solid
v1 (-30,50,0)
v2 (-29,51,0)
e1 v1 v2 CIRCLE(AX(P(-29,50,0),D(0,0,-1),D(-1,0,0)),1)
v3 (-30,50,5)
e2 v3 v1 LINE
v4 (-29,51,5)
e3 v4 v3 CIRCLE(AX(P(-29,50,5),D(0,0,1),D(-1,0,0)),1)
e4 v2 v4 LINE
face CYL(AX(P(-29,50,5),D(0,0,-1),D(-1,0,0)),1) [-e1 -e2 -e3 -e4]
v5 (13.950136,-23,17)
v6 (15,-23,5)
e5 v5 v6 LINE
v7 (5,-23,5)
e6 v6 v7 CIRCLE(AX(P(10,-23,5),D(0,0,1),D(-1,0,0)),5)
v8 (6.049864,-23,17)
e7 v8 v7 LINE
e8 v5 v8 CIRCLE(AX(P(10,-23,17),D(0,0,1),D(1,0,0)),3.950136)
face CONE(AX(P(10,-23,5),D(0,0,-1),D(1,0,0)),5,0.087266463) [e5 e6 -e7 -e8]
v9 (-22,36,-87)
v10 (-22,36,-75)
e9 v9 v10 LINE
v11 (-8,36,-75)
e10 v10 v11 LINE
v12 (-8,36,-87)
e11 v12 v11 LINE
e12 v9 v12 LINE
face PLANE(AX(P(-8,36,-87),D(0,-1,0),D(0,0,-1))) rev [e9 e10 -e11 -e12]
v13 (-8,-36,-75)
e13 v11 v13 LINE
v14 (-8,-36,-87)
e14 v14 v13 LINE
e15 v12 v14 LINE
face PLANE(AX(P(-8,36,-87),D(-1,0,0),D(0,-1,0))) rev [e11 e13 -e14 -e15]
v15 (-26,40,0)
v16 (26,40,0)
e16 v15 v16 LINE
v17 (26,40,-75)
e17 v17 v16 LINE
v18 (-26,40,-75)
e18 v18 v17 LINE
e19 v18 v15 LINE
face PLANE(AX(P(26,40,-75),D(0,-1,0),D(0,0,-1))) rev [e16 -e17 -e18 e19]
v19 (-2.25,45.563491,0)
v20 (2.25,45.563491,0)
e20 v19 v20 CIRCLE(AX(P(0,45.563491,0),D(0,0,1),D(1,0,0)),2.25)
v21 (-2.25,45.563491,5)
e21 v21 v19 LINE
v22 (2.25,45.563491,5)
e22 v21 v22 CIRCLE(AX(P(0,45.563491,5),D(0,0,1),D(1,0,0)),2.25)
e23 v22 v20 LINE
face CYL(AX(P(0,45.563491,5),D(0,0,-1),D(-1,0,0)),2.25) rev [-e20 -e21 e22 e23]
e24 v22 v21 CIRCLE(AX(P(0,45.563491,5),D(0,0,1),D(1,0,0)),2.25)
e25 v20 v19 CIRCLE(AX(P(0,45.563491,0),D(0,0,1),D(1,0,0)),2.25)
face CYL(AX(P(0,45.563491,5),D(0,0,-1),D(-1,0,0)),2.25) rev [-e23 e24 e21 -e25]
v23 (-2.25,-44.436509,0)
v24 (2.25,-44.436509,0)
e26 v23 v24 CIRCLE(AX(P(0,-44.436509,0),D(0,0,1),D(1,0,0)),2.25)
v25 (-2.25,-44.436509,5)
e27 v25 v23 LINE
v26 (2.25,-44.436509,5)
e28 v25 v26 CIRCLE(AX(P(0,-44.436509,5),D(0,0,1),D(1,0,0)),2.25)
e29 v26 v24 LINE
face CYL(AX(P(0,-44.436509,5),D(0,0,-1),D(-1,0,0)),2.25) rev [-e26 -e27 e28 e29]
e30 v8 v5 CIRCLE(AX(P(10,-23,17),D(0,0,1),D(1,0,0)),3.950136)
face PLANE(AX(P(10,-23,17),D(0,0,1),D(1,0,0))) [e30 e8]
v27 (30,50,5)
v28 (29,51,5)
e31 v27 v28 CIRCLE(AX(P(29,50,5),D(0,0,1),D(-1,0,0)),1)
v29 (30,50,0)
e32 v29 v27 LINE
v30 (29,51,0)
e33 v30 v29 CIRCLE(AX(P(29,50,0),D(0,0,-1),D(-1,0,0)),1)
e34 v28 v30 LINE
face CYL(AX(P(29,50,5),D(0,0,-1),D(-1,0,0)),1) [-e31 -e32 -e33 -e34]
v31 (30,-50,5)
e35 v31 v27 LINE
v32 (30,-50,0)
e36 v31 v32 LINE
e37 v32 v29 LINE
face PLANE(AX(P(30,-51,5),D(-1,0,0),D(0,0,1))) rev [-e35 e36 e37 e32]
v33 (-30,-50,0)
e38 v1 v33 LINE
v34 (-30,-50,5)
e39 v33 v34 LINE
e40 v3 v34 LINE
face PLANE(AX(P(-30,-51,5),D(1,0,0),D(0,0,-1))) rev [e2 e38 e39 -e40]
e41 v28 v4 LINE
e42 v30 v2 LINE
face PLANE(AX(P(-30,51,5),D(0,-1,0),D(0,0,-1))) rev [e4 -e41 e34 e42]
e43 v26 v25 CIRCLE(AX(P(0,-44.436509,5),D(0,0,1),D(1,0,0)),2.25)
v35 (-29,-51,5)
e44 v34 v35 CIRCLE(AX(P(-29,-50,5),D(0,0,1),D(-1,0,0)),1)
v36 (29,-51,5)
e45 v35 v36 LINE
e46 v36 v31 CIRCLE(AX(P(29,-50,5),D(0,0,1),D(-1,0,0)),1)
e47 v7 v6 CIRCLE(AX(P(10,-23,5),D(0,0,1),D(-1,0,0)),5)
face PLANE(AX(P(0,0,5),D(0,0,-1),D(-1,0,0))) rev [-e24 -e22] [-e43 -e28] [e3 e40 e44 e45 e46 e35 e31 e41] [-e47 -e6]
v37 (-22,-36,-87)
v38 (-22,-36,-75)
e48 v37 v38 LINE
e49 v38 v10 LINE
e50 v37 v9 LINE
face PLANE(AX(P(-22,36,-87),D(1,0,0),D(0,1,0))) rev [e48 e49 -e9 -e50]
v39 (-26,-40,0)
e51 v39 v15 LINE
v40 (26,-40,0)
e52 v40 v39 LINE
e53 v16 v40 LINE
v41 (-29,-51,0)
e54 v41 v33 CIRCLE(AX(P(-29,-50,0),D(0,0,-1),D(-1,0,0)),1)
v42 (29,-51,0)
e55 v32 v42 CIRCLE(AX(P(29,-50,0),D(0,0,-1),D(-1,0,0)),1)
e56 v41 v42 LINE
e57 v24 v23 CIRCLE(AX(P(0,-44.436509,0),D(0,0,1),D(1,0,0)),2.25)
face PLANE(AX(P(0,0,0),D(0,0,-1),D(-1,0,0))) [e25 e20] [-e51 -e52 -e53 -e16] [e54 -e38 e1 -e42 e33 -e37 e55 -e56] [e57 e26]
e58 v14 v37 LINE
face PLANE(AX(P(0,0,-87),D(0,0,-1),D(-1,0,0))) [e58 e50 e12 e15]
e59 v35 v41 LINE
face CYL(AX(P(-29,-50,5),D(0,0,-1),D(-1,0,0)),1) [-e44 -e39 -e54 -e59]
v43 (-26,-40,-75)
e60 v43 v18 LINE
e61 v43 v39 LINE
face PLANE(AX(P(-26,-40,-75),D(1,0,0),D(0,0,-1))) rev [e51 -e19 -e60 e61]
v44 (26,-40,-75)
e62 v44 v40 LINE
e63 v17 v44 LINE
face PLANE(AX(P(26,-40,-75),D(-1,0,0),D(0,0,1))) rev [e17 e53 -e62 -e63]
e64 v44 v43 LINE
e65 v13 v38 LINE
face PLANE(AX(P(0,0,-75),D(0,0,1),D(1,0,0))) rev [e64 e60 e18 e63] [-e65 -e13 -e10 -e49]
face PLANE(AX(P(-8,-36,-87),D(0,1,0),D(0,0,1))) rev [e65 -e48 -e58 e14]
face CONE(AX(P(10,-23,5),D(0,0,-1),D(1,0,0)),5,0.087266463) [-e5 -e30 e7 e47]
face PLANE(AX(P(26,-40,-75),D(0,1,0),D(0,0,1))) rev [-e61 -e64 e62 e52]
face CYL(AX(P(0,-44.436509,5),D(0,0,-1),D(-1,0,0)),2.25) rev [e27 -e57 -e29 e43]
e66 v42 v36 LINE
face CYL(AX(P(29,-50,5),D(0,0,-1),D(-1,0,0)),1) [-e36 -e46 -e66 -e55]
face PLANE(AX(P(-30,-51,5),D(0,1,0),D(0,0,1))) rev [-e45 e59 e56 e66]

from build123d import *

# Parameters (mm, degrees)
SKETCH_1_W      = 60
SKETCH_1_H      = 102
SKETCH_1_R      = 2.25
EXTRUDE_1_DEPTH = 5
SKETCH_2_W      = 52
SKETCH_2_H      = 80
EXTRUDE_2_DEPTH = 75
SKETCH_3_R      = 5
EXTRUDE_3_DEPTH = 12
EXTRUDE_3_TAPER = 5
FILLET_1_R      = 1
SKETCH_4_W      = 14
SKETCH_4_H      = 72
EXTRUDE_4_DEPTH = 12


with BuildPart() as part:
    # 草图1 → 凸台-拉伸1 (new body)
    with BuildSketch(Plane.XY):
        Rectangle(SKETCH_1_W, SKETCH_1_H)
        with Locations((0, 45.563491435)):
            Circle(SKETCH_1_R, mode=Mode.SUBTRACT)
        with Locations((0, -44.436508565)):
            Circle(SKETCH_1_R, mode=Mode.SUBTRACT)
    extrude(amount=EXTRUDE_1_DEPTH)

    # 草图2 → 凸台-拉伸2 (add)
    with BuildSketch(Plane(origin=(0, 0, 0), x_dir=(-1, 0, 0), z_dir=(0, 0, -1))):
        Rectangle(SKETCH_2_W, SKETCH_2_H)
    extrude(amount=EXTRUDE_2_DEPTH)

    # 草图3 → 凸台-拉伸3 (add)
    with BuildSketch(Plane.XY.offset(5)):
        with Locations((10, -23)):
            Circle(SKETCH_3_R)
    extrude(amount=EXTRUDE_3_DEPTH, taper=EXTRUDE_3_TAPER)

    # 圆角1
    fillet_1_edges = [part.edges().sort_by_distance(p)[0] for p in [
        (30, -51, 2.5),
        (-30, -51, 2.5),
        (-30, 51, 2.5),
        (30, 51, 2.5),
    ]]
    fillet(fillet_1_edges, radius=FILLET_1_R)

    # 草图4 → 凸台-拉伸4 (add)
    with BuildSketch(Plane(origin=(0, 0, -75), x_dir=(-1, 0, 0), z_dir=(0, 0, -1))):
        with Locations((15, 0)):
            Rectangle(SKETCH_4_W, SKETCH_4_H)
    extrude(amount=EXTRUDE_4_DEPTH)


solid = part.part
